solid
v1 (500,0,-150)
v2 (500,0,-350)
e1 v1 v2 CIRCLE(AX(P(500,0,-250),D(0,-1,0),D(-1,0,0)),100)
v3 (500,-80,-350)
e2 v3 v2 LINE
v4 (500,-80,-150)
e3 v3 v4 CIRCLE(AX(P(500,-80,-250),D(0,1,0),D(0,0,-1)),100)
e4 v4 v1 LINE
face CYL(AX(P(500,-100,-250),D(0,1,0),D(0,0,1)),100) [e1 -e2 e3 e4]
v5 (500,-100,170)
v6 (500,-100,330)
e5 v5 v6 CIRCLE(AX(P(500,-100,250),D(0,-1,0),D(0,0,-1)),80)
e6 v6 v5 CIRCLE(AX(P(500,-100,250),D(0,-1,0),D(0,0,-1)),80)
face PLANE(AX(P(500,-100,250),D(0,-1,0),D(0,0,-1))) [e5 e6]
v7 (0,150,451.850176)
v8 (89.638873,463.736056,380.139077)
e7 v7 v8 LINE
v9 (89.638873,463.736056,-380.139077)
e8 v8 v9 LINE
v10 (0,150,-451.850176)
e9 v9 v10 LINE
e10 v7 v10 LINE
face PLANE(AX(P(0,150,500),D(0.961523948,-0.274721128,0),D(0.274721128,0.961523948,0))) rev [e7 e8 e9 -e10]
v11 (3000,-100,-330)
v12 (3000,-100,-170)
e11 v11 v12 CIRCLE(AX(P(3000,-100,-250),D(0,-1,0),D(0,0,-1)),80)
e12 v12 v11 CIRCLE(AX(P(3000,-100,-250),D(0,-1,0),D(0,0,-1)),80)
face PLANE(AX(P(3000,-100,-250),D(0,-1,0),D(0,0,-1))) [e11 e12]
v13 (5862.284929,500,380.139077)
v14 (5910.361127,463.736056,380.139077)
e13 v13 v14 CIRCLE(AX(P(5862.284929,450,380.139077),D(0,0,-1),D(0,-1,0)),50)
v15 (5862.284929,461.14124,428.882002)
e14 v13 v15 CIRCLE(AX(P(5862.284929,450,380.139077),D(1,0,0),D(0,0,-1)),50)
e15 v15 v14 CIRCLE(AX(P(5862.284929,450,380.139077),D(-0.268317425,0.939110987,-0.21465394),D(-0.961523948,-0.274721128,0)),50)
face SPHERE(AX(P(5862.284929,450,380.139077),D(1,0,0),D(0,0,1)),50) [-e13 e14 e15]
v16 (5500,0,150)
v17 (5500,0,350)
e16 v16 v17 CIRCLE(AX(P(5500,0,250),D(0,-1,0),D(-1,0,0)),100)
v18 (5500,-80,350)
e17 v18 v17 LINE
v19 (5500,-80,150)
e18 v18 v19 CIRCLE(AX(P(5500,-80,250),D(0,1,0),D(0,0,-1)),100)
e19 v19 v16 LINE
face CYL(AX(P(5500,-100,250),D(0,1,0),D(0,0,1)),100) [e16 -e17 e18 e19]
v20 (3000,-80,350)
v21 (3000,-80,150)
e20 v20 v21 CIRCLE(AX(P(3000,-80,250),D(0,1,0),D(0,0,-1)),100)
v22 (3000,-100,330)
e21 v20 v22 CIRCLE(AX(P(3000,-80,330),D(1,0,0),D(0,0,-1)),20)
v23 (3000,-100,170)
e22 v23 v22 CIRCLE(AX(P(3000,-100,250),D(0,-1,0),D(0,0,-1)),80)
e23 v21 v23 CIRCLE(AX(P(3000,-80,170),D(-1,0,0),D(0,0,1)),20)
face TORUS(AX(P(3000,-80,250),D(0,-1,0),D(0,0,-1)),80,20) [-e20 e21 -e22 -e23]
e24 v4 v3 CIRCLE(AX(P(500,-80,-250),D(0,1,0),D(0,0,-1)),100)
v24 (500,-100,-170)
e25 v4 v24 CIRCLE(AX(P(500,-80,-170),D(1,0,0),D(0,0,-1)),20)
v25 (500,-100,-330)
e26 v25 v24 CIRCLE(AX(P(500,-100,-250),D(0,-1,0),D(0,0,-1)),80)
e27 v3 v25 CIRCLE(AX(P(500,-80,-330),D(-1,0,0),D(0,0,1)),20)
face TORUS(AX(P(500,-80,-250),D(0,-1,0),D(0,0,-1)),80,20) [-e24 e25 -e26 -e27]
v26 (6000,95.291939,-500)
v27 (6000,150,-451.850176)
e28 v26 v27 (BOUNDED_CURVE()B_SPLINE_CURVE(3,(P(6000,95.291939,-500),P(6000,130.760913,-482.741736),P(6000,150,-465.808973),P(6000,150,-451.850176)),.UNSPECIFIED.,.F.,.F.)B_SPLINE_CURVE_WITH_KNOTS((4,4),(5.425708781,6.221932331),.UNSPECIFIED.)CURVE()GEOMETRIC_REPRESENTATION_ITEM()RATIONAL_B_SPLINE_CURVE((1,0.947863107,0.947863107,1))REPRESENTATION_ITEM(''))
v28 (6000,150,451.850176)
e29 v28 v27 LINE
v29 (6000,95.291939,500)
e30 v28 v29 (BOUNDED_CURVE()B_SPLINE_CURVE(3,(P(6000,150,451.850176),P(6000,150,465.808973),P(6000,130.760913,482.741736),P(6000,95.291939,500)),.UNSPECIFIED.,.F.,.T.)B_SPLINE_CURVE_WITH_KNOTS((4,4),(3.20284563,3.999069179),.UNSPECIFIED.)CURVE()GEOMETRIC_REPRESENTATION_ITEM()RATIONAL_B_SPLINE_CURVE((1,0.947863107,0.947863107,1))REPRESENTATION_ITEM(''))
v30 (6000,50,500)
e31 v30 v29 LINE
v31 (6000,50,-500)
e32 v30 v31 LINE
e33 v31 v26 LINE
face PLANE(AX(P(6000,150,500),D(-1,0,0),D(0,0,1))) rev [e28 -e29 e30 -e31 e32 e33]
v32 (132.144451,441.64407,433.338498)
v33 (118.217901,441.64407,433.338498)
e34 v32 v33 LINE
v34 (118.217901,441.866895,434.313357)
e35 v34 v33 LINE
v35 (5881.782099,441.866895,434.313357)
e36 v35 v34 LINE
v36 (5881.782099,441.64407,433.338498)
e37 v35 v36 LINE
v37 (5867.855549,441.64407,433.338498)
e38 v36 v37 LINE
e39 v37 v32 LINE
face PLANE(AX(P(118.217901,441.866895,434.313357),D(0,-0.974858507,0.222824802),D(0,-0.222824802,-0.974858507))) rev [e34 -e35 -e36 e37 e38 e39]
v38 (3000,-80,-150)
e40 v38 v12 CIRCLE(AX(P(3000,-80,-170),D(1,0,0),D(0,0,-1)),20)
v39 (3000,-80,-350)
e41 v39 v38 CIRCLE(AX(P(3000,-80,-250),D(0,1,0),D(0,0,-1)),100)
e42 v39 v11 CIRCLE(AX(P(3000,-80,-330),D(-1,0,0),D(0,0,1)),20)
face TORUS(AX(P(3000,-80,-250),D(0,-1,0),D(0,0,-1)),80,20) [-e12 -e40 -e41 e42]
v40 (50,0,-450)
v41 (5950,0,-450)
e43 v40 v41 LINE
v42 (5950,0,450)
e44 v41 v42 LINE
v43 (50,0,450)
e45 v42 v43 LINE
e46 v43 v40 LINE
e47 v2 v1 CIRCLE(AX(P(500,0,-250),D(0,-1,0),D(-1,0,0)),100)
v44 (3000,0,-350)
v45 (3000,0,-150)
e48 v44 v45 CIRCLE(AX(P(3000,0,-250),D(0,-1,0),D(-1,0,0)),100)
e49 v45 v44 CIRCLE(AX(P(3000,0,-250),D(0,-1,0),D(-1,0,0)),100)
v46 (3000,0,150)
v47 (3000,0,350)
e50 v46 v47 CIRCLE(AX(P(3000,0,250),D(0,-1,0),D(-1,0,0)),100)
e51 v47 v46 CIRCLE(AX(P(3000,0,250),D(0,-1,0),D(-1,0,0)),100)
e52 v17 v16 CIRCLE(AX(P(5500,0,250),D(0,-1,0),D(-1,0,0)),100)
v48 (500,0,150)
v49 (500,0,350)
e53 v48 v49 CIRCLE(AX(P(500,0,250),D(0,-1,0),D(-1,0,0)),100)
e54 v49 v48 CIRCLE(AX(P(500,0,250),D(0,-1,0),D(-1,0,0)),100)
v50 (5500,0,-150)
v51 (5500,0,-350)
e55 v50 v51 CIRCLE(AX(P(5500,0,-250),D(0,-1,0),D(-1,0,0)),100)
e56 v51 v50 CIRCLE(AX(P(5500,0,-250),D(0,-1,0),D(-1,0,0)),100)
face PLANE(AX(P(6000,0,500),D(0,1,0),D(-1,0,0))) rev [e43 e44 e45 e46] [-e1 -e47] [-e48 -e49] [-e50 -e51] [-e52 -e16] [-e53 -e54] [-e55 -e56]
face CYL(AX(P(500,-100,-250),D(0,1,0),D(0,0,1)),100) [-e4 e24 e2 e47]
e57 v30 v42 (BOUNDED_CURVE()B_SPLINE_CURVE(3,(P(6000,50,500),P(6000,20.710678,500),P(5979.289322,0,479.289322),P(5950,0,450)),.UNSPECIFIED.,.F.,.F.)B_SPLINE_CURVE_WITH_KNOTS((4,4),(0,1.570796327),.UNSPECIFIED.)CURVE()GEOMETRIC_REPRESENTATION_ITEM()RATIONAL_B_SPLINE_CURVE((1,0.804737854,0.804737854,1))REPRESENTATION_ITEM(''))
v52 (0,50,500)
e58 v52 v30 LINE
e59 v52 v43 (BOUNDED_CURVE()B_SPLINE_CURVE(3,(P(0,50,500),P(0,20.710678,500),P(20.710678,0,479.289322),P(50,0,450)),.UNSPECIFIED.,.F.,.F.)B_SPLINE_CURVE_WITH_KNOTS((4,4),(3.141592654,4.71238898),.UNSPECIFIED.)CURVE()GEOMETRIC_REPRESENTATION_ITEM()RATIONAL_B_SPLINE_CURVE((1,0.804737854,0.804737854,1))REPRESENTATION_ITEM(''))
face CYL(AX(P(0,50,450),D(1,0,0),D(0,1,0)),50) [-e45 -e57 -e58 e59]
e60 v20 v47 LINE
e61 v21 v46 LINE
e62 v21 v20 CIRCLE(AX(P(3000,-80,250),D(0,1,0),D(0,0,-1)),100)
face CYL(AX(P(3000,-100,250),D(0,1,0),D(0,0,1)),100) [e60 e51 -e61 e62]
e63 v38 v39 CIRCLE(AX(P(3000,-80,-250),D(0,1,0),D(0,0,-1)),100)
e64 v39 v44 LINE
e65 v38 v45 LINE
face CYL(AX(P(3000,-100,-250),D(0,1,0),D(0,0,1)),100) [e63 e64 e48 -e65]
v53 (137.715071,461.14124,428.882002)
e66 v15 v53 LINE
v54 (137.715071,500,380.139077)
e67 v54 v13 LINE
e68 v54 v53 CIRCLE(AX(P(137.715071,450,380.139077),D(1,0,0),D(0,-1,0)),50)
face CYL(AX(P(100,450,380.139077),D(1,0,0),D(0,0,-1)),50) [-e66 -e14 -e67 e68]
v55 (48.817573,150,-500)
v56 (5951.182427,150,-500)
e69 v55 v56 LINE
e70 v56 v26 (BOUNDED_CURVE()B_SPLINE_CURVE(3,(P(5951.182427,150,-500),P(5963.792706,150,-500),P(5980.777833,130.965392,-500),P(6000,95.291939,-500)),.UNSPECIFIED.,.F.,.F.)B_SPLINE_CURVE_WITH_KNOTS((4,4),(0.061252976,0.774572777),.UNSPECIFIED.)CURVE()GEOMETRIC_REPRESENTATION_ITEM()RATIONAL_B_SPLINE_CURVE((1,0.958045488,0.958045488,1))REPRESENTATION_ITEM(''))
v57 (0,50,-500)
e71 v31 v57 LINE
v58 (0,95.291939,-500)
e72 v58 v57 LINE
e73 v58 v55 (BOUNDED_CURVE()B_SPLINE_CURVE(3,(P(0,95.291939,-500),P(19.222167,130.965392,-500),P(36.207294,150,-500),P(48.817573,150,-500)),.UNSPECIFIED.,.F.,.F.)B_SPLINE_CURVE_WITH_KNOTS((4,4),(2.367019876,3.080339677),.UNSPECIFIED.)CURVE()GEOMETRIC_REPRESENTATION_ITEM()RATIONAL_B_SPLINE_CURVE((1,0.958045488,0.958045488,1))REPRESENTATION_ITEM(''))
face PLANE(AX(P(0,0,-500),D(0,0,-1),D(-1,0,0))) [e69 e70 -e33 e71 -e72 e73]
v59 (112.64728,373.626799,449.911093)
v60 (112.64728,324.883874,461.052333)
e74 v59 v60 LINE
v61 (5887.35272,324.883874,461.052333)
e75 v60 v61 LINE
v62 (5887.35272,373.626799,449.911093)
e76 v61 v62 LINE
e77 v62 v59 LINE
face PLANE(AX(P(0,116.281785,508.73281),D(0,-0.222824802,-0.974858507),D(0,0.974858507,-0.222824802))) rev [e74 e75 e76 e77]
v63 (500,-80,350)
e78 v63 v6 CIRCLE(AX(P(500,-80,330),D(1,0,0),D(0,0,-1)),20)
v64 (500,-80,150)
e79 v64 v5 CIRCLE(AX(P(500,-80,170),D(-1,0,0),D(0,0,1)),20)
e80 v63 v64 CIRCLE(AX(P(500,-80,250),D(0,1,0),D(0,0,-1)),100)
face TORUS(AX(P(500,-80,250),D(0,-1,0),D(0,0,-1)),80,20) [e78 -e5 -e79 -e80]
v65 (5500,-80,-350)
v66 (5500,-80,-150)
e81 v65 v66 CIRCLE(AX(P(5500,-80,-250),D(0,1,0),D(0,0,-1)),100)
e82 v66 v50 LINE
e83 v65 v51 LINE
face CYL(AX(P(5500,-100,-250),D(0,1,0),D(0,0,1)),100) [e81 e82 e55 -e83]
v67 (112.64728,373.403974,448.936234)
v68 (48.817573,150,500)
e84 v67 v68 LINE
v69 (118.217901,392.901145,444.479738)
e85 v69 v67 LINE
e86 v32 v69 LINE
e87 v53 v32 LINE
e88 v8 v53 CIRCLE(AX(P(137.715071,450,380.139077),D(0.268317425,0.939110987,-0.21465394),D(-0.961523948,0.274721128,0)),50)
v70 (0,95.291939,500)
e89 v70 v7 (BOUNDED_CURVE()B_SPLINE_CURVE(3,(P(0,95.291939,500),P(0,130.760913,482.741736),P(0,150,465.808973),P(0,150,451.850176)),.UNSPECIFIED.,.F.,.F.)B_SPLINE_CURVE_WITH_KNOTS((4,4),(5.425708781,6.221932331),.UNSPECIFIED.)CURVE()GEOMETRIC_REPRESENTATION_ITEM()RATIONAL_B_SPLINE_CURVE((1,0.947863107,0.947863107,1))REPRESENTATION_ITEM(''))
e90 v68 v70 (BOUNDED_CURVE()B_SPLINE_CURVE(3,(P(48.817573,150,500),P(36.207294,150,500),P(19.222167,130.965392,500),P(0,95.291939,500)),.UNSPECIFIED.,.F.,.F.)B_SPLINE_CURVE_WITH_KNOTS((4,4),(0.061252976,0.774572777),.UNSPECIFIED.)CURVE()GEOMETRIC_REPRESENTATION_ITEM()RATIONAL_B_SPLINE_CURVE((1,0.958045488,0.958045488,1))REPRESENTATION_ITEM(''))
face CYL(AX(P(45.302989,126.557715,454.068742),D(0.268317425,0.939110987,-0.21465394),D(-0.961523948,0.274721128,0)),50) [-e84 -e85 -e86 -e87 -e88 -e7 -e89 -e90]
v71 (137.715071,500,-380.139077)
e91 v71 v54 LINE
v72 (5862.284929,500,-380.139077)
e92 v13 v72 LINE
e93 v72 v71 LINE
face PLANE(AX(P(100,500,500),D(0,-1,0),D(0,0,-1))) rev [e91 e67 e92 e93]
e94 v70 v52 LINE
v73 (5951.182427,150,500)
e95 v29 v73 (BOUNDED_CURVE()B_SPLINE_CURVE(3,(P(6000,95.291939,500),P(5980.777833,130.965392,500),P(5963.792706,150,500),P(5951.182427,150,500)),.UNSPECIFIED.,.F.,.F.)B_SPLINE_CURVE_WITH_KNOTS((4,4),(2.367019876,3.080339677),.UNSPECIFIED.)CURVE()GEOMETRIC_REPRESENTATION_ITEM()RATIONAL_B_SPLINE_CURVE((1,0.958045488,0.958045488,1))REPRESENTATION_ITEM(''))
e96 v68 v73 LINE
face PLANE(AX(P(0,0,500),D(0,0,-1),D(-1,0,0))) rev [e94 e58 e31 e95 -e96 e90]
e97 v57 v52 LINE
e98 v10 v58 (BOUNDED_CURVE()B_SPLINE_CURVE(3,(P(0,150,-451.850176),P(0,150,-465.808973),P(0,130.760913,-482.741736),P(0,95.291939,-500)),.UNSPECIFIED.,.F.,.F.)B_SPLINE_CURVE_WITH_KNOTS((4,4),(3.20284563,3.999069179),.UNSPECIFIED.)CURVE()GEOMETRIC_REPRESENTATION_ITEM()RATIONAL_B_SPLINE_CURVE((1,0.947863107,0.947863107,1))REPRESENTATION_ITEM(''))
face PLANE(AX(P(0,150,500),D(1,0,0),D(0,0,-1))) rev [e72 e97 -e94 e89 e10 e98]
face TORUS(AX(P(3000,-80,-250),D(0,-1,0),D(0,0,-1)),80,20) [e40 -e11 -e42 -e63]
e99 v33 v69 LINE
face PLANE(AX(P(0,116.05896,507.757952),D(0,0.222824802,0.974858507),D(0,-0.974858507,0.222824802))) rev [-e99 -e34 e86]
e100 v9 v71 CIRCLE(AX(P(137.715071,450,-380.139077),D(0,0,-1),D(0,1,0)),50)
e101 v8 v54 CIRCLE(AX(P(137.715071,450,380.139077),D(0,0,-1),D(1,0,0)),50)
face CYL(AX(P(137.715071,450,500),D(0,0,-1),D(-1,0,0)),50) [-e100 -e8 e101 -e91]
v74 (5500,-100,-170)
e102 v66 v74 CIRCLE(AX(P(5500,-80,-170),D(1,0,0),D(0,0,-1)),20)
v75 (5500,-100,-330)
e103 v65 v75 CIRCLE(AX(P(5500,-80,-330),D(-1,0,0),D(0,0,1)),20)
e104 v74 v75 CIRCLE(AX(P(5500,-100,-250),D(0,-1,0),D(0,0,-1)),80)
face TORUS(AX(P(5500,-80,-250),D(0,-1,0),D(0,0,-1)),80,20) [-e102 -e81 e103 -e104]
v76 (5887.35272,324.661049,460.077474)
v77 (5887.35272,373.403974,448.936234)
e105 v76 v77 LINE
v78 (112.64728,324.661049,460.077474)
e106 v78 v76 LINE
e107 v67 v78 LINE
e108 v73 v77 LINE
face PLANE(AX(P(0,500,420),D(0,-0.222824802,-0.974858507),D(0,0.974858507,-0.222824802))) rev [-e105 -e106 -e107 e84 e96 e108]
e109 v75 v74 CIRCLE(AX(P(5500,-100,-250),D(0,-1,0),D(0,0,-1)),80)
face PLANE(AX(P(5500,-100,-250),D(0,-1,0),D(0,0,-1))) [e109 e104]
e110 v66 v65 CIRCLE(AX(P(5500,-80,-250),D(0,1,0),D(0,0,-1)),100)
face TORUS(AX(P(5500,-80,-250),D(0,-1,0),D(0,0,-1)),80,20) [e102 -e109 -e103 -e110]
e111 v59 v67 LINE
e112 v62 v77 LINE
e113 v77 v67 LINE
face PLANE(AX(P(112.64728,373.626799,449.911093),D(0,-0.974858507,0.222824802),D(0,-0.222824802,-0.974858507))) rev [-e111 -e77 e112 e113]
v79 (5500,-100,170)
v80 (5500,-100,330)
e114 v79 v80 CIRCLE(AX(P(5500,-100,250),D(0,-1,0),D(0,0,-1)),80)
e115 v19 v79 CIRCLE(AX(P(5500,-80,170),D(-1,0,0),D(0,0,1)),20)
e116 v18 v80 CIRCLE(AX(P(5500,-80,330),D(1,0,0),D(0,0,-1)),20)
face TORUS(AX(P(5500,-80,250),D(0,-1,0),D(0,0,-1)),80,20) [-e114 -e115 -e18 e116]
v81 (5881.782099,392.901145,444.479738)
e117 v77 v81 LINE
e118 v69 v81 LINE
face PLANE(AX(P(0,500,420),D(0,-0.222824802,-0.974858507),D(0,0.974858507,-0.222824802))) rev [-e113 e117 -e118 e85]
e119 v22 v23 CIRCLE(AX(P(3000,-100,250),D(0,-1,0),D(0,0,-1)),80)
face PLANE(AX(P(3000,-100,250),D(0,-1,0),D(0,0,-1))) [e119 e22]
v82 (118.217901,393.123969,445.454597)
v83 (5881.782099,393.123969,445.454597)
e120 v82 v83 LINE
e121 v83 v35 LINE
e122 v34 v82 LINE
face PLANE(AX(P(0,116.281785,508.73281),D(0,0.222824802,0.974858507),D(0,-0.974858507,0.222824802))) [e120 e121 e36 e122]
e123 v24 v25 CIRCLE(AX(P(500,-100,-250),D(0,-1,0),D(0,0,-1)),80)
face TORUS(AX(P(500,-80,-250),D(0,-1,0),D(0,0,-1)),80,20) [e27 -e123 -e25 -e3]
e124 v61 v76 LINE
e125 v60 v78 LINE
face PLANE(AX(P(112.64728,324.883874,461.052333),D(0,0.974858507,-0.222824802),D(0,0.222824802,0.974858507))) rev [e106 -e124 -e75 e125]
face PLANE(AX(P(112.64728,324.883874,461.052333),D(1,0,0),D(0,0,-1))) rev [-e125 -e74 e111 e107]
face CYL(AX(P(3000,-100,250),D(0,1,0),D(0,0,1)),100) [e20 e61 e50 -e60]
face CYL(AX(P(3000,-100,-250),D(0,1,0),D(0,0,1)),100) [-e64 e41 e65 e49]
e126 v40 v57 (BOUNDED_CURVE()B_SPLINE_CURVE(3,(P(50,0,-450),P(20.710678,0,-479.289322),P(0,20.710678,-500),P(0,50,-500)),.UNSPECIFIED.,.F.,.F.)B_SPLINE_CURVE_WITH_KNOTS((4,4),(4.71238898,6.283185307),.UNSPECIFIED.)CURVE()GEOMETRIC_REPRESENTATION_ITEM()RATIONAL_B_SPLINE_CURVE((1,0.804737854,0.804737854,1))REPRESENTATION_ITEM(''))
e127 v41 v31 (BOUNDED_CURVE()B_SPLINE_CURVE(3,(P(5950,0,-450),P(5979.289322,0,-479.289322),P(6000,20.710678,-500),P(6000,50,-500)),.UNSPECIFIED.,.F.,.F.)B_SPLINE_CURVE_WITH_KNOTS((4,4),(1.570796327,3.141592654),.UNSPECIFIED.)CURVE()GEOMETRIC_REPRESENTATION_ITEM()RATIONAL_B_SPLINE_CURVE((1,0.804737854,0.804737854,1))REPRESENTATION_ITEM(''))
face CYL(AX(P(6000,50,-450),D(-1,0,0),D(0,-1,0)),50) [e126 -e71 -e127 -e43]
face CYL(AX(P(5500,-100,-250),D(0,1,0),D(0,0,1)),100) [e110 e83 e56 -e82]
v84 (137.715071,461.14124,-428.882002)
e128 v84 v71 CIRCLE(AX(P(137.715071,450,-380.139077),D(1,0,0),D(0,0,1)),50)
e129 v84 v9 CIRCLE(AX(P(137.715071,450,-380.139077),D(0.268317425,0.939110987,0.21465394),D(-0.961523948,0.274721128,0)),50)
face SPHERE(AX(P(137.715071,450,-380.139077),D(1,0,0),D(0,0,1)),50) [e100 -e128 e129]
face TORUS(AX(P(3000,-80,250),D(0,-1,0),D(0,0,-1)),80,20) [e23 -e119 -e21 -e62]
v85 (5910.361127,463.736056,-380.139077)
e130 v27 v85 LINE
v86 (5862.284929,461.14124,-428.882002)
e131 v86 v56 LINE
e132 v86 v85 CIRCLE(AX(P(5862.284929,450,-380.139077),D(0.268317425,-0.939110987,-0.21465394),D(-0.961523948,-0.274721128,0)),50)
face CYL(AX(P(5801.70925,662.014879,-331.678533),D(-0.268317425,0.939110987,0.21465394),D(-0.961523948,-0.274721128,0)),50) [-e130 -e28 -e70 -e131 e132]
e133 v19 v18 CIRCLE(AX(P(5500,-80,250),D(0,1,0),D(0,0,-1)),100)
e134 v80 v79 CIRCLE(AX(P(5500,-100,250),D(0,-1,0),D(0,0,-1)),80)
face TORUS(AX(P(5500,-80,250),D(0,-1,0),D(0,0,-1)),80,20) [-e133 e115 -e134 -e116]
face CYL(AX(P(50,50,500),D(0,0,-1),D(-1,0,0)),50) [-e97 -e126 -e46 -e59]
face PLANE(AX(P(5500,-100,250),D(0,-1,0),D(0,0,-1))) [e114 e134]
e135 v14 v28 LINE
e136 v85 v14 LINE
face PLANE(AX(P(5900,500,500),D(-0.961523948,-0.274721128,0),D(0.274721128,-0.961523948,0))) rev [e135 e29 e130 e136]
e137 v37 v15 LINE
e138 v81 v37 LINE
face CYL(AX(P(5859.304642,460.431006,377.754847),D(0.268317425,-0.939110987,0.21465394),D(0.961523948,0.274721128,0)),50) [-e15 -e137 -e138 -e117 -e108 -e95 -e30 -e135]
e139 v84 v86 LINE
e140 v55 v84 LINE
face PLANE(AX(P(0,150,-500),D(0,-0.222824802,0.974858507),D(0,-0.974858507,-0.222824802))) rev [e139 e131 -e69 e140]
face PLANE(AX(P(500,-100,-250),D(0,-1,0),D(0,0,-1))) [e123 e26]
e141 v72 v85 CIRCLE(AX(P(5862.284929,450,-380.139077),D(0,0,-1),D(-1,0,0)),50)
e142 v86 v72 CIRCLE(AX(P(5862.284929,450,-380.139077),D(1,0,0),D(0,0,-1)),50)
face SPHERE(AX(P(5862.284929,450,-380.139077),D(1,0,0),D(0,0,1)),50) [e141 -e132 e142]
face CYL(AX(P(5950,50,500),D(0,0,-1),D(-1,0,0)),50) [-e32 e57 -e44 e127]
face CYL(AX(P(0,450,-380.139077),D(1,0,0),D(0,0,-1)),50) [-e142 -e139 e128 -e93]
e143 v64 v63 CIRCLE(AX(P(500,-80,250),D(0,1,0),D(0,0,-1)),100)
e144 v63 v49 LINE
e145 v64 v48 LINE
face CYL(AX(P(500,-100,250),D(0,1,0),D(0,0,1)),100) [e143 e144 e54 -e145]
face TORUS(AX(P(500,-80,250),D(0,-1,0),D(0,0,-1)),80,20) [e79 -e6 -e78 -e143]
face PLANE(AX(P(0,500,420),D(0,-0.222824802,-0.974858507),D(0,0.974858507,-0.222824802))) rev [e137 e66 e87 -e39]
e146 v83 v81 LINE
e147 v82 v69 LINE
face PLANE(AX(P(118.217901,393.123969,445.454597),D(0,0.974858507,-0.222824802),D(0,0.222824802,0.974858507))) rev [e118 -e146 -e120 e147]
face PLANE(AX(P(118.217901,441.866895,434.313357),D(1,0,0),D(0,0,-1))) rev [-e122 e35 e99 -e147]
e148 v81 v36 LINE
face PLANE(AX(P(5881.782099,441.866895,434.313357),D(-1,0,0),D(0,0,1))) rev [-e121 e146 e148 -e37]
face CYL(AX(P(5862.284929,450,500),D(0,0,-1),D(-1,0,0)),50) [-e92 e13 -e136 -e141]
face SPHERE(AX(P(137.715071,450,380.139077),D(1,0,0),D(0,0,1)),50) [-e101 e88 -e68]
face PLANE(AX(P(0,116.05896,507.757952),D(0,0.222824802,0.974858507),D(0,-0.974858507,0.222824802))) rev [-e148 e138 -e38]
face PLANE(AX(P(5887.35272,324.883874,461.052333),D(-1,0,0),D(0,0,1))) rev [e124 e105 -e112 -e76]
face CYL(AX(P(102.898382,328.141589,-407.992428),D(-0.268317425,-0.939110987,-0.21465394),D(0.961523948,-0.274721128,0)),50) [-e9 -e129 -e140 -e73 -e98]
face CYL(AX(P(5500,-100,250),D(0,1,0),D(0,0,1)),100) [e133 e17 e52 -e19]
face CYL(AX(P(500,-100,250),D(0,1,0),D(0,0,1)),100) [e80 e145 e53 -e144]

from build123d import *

# Parameters (mm, degrees)
BOSS_EXTRUDE1_DEPTH     = 500
SKETCH4_R               = 100
BOSS_EXTRUDE2_DEPTH     = 100
CUT_EXTRUDE3_DEPTH      = 6042.522986797
CUT_EXTRUDE3_DEPTH_BACK = 6042.522986797
FILLET1_R               = 50
FILLET2_R               = 20
SKETCH8_W               = 5763.564198988
SKETCH8_H               = 50
SKETCH8_W_2             = 5774.705439062
BOSS_EXTRUDE3_DEPTH     = 1


with BuildPart() as part:
    # Sketch1 → Boss-Extrude1 (new, symmetric)
    with BuildSketch(Plane.XY):
        Polygon((100, 500), (5900, 500), (6000, 150), (6000, 0), (0, 0), (0, 150), align=None)
    extrude(amount=BOSS_EXTRUDE1_DEPTH, both=True)

    # Sketch4 → Boss-Extrude2 (add)
    with BuildSketch(Plane(origin=(0, 0, 0), x_dir=(-1, 0, 0), z_dir=(0, -1, 0))):
        with Locations((-500, -250)):
            Circle(SKETCH4_R)
        with Locations((-500, 250)):
            Circle(SKETCH4_R)
        with Locations((-5500, 250)):
            Circle(SKETCH4_R)
        with Locations((-5500, -250)):
            Circle(SKETCH4_R)
        with Locations((-3000, -250)):
            Circle(SKETCH4_R)
        with Locations((-3000, 250)):
            Circle(SKETCH4_R)
    extrude(amount=BOSS_EXTRUDE2_DEPTH)

    # Sketch5 → Cut-Extrude3 (cut, two sides: drawn at the far end of the back side and taken through both)
    with BuildSketch(Plane(origin=(6000, 0, 0), x_dir=(0, 0, -1), z_dir=(1, 0, 0)).offset(-CUT_EXTRUDE3_DEPTH_BACK)):
        Polygon((-420, 500), (-500, 150), (-500, 500), align=None)
        Polygon((500, 500), (500, 150), (420, 500), align=None)
    extrude(amount=CUT_EXTRUDE3_DEPTH + CUT_EXTRUDE3_DEPTH_BACK, mode=Mode.SUBTRACT)

    # Fillet1
    fillet1_edges = [part.edges().sort_by_distance(p)[0] for p in [
        (5900, 500, 0),
        (100, 500, 0),
        (6000, 0, 0),
        (3000, 0, -500),
        (3000, 0, 500),
        (0, 0, 0),
        (5950, 325, -460),
        (5950, 325, 460),
        (50, 325, 460),
        (50, 325, -460),
        (3000, 500, -420),
        (3000, 500, 420),
    ]]
    fillet(fillet1_edges, radius=FILLET1_R)

    # Fillet2
    fillet2_edges = [part.edges().sort_by_distance(p)[0] for p in [
        (600, -100, 250),
        (600, -100, -250),
        (5600, -100, -250),
        (5600, -100, 250),
        (3100, -100, 250),
        (3100, -100, -250),
    ]]
    fillet(fillet2_edges, radius=FILLET2_R)

    # Sketch8 → Boss-Extrude3 (add)
    with BuildSketch(Plane(origin=(0, 116.058960434, 507.757951901), x_dir=(1, 0, 0), z_dir=(0, 0.22282480150214157, 0.9748585065718672))):
        with Locations((3000, 308.981913595)):
            Rectangle(SKETCH8_W, SKETCH8_H)
        with Locations((3000, 238.981913595)):
            Rectangle(SKETCH8_W_2, SKETCH8_H)
    extrude(amount=BOSS_EXTRUDE3_DEPTH)


solid = part.part
